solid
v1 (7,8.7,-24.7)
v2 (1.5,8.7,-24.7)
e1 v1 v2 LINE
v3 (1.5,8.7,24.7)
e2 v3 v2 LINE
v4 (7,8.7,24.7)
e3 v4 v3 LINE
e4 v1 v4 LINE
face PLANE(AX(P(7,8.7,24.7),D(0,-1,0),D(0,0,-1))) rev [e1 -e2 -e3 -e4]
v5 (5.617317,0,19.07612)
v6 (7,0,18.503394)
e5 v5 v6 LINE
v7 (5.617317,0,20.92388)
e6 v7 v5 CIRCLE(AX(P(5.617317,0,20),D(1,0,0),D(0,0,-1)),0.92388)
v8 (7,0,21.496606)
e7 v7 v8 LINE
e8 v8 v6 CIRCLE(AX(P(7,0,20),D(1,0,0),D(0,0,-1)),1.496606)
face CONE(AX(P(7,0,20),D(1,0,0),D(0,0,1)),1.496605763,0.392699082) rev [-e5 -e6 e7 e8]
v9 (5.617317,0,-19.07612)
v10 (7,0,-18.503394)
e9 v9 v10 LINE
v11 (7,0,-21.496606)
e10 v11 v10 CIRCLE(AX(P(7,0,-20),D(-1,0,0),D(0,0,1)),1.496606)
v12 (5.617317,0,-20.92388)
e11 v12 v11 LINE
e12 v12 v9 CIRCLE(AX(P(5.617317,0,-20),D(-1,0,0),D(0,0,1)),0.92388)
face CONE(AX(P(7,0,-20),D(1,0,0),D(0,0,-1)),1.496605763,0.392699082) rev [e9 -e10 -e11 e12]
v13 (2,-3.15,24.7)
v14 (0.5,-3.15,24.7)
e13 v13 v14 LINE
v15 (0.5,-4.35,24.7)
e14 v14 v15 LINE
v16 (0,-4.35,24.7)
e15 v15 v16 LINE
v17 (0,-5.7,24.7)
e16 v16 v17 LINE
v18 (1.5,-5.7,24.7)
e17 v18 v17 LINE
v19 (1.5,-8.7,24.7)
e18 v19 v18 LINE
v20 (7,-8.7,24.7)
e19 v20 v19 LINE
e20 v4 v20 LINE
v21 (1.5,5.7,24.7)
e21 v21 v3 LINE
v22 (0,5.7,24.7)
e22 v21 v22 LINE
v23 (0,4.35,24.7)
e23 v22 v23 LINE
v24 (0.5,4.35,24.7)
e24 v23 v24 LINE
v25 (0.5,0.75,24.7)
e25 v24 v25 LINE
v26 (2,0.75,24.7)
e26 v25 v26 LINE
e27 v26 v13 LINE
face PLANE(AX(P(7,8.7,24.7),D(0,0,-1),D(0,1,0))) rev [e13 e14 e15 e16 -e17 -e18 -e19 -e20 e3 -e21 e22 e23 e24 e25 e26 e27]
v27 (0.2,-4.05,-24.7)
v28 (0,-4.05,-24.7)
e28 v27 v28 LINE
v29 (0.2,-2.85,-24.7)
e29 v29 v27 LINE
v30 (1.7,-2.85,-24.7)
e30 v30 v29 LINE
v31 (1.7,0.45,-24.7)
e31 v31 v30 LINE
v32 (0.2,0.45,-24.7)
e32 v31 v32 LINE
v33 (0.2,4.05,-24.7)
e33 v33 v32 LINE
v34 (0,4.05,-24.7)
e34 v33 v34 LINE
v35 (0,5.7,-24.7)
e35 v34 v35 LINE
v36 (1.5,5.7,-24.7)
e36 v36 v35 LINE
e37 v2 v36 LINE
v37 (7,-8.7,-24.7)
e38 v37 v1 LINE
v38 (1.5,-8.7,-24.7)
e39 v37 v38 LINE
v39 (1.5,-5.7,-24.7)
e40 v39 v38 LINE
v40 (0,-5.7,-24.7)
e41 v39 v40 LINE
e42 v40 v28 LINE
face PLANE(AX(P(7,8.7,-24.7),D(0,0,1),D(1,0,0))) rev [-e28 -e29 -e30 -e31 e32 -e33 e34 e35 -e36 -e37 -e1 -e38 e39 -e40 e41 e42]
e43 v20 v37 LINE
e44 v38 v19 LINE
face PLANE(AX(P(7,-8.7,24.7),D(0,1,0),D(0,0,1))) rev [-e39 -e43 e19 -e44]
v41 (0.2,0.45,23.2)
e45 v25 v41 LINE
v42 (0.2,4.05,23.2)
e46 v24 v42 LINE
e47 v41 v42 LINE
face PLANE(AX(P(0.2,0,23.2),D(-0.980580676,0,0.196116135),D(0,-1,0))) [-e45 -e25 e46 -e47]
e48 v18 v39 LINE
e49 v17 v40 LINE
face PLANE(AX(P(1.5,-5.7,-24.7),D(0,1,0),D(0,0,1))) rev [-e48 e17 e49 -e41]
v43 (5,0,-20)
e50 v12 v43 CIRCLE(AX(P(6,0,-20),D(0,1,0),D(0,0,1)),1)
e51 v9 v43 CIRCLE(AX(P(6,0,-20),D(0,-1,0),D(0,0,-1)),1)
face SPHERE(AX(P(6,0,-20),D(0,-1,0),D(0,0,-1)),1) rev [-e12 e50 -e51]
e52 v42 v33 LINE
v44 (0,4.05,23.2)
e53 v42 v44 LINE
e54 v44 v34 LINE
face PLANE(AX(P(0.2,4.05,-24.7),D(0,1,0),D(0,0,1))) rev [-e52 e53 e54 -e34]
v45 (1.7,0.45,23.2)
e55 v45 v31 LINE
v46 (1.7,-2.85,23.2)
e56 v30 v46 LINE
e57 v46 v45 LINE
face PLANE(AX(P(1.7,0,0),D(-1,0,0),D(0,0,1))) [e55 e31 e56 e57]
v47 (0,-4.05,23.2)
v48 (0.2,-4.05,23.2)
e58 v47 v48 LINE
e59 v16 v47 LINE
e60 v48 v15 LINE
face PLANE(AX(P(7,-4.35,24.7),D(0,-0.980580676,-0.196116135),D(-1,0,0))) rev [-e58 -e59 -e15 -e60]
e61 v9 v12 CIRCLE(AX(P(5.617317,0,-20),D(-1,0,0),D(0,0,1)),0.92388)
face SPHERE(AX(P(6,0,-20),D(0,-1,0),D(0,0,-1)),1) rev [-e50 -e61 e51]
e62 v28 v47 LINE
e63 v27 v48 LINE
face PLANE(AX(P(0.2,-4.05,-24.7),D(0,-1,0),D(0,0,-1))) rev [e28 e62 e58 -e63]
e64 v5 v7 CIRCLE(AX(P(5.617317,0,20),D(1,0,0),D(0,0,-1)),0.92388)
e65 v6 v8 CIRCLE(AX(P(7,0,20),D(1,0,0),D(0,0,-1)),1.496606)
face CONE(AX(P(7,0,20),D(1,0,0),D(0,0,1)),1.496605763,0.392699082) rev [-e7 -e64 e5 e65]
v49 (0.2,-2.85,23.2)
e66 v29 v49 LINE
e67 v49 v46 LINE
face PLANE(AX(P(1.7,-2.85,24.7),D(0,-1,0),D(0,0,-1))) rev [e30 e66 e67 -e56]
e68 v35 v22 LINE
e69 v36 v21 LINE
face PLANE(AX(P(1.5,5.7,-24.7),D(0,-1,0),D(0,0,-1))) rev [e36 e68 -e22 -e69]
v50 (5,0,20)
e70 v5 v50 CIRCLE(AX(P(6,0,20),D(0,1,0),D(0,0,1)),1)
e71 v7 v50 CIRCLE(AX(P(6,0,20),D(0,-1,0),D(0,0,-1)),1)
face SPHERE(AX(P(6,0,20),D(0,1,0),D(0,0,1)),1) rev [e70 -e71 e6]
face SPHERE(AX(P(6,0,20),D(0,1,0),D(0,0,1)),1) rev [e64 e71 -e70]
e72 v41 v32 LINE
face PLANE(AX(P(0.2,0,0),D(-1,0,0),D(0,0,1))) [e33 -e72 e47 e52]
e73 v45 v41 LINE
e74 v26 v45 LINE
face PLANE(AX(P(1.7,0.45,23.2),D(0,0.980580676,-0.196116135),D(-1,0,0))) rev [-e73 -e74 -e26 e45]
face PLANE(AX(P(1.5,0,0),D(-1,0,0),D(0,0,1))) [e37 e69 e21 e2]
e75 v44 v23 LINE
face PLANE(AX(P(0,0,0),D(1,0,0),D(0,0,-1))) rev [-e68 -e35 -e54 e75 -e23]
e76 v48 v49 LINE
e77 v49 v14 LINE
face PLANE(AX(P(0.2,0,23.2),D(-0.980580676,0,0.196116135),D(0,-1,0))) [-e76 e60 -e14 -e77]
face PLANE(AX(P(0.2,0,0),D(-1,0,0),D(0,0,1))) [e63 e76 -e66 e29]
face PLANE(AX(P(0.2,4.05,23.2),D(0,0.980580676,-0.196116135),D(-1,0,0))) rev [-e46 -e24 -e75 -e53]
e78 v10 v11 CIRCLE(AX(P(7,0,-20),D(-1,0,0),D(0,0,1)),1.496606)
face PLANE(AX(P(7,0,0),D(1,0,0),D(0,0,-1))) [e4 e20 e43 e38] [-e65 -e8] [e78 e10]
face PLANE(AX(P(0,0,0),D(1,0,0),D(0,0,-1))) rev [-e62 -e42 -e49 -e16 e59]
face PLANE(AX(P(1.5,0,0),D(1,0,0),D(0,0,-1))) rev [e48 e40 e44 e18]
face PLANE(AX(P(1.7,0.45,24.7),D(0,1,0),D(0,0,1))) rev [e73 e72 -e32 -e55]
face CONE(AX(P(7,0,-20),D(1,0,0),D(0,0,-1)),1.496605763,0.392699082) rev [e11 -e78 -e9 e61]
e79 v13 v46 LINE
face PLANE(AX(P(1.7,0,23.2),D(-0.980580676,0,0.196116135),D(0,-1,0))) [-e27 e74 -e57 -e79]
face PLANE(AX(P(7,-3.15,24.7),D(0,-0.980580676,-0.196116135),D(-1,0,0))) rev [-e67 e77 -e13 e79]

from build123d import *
from OCP.BRepFilletAPI import BRepFilletAPI_MakeChamfer

# Parameters (mm, degrees)
SKETCH1_W           = 49.4
SKETCH1_H           = 17.4
BOSS_EXTRUDE1_DEPTH = 7
SKETCH2_W           = 49.4
SKETCH2_H           = 8.1
CUT_EXTRUDE1_DEPTH  = 0.2
SKETCH3_W           = 49.4
SKETCH3_H           = 3.3
CUT_EXTRUDE2_DEPTH  = 1.7
SKETCH5_W           = 49.4
SKETCH5_H           = 3
CUT_EXTRUDE3_DEPTH  = 1.5
CHAMFER1_SIZE       = 1.5
CHAMFER1_SIZE2      = 0.3
CHAMFER2_SIZE       = 0.3
CHAMFER2_SIZE2      = 1.5


with BuildPart() as part:
    # Sketch1 → Boss-Extrude1 (new body)
    with BuildSketch(Plane(origin=(0, 0, 0), x_dir=(0, 0, -1), z_dir=(1, 0, 0))):
        Rectangle(SKETCH1_W, SKETCH1_H)
    extrude(amount=BOSS_EXTRUDE1_DEPTH)

    # Sketch2 → Cut-Extrude1 (cut)
    with BuildSketch(Plane.ZY):
        Rectangle(SKETCH2_W, SKETCH2_H)
    extrude(amount=-CUT_EXTRUDE1_DEPTH, mode=Mode.SUBTRACT)

    # Sketch3 → Cut-Extrude2 (cut)
    with BuildSketch(Plane.ZY):
        with Locations((0, -1.2)):
            Rectangle(SKETCH3_W, SKETCH3_H)
    extrude(amount=-CUT_EXTRUDE2_DEPTH, mode=Mode.SUBTRACT)

    # Sketch4 → Cut-Revolve1 (revolve, cut)
    with BuildSketch(Plane(origin=(0, 0, 0), x_dir=(1, 0, 0), z_dir=(0, 1, 0))):
        with BuildLine():
            Line((5.617316568, 20.923879533), (7, 21.496605763))
            Line((7, 21.496605763), (7, 20))
            Line((7, 20), (5, 20))
            ThreePointArc((5, 20), (5.168530388, 20.555570233), (5.617316568, 20.923879533))
        make_face()
    cut_revolve1 = revolve(axis=Axis((9.957130438, 0, -20), (1, 0, 0)), mode=Mode.SUBTRACT)

    # Mirror1: Cut-Revolve1 across plane
    add(cut_revolve1.mirror(Plane.XY), mode=Mode.SUBTRACT)

    # Sketch5 → Cut-Extrude3 (cut)
    with BuildSketch(Plane.ZY):
        with Locations((0, 7.2)):
            Rectangle(SKETCH5_W, SKETCH5_H)
        with Locations((0, -7.2)):
            Rectangle(SKETCH5_W, SKETCH5_H)
    extrude(amount=-CUT_EXTRUDE3_DEPTH, mode=Mode.SUBTRACT)

    # Chamfer1: one chamfer whose edges measure the first distance from different faces: ONE call of the kernel's chamfer builder (chamfer() names one face for all edges)
    chamfer1_edges_1 = [part.edges().sort_by_distance(p)[0] for p in [
        (0.2, -3.45, 24.7),
    ]]
    chamfer1_side_1 = [part.faces().sort_by_distance(p)[0] for p in [
        (0.2, -3.45, 0),
    ]]
    chamfer1_edges_2 = [part.edges().sort_by_distance(p)[0] for p in [
        (0.1, -4.05, 24.7),
    ]]
    chamfer1_side_2 = [part.faces().sort_by_distance(p)[0] for p in [
        (0.1, -4.05, 0),
    ]]
    chamfer1_edges_3 = [part.edges().sort_by_distance(p)[0] for p in [
        (0.95, -2.85, 24.7),
    ]]
    chamfer1_side_3 = [part.faces().sort_by_distance(p)[0] for p in [
        (0.95, -2.85, 0),
    ]]
    chamfer1 = BRepFilletAPI_MakeChamfer(part.part.solid().wrapped)
    for e in chamfer1_edges_1:
        chamfer1.Add(CHAMFER1_SIZE, CHAMFER1_SIZE2, e.wrapped, chamfer1_side_1[0].wrapped)  # the first distance lies on this face
    for e in chamfer1_edges_2:
        chamfer1.Add(CHAMFER1_SIZE, CHAMFER1_SIZE2, e.wrapped, chamfer1_side_2[0].wrapped)  # the first distance lies on this face
    for e in chamfer1_edges_3:
        chamfer1.Add(CHAMFER1_SIZE, CHAMFER1_SIZE2, e.wrapped, chamfer1_side_3[0].wrapped)  # the first distance lies on this face
    add(Compound.cast(chamfer1.Shape()), mode=Mode.REPLACE)

    # Chamfer2
    chamfer2_edges = [part.edges().sort_by_distance(p)[0] for p in [
        (1.7, -1.35, 24.7),
        (0.1, 4.05, 24.7),
        (0.2, 2.25, 24.7),
        (0.95, 0.45, 24.7),
    ]]
    chamfer2_side = [part.faces().sort_by_distance(p)[0] for p in [
        (3.930580866, 0.084396355, 24.7),
    ]]
    chamfer(chamfer2_edges, length=CHAMFER2_SIZE, length2=CHAMFER2_SIZE2, reference=chamfer2_side[0])


solid = part.part
